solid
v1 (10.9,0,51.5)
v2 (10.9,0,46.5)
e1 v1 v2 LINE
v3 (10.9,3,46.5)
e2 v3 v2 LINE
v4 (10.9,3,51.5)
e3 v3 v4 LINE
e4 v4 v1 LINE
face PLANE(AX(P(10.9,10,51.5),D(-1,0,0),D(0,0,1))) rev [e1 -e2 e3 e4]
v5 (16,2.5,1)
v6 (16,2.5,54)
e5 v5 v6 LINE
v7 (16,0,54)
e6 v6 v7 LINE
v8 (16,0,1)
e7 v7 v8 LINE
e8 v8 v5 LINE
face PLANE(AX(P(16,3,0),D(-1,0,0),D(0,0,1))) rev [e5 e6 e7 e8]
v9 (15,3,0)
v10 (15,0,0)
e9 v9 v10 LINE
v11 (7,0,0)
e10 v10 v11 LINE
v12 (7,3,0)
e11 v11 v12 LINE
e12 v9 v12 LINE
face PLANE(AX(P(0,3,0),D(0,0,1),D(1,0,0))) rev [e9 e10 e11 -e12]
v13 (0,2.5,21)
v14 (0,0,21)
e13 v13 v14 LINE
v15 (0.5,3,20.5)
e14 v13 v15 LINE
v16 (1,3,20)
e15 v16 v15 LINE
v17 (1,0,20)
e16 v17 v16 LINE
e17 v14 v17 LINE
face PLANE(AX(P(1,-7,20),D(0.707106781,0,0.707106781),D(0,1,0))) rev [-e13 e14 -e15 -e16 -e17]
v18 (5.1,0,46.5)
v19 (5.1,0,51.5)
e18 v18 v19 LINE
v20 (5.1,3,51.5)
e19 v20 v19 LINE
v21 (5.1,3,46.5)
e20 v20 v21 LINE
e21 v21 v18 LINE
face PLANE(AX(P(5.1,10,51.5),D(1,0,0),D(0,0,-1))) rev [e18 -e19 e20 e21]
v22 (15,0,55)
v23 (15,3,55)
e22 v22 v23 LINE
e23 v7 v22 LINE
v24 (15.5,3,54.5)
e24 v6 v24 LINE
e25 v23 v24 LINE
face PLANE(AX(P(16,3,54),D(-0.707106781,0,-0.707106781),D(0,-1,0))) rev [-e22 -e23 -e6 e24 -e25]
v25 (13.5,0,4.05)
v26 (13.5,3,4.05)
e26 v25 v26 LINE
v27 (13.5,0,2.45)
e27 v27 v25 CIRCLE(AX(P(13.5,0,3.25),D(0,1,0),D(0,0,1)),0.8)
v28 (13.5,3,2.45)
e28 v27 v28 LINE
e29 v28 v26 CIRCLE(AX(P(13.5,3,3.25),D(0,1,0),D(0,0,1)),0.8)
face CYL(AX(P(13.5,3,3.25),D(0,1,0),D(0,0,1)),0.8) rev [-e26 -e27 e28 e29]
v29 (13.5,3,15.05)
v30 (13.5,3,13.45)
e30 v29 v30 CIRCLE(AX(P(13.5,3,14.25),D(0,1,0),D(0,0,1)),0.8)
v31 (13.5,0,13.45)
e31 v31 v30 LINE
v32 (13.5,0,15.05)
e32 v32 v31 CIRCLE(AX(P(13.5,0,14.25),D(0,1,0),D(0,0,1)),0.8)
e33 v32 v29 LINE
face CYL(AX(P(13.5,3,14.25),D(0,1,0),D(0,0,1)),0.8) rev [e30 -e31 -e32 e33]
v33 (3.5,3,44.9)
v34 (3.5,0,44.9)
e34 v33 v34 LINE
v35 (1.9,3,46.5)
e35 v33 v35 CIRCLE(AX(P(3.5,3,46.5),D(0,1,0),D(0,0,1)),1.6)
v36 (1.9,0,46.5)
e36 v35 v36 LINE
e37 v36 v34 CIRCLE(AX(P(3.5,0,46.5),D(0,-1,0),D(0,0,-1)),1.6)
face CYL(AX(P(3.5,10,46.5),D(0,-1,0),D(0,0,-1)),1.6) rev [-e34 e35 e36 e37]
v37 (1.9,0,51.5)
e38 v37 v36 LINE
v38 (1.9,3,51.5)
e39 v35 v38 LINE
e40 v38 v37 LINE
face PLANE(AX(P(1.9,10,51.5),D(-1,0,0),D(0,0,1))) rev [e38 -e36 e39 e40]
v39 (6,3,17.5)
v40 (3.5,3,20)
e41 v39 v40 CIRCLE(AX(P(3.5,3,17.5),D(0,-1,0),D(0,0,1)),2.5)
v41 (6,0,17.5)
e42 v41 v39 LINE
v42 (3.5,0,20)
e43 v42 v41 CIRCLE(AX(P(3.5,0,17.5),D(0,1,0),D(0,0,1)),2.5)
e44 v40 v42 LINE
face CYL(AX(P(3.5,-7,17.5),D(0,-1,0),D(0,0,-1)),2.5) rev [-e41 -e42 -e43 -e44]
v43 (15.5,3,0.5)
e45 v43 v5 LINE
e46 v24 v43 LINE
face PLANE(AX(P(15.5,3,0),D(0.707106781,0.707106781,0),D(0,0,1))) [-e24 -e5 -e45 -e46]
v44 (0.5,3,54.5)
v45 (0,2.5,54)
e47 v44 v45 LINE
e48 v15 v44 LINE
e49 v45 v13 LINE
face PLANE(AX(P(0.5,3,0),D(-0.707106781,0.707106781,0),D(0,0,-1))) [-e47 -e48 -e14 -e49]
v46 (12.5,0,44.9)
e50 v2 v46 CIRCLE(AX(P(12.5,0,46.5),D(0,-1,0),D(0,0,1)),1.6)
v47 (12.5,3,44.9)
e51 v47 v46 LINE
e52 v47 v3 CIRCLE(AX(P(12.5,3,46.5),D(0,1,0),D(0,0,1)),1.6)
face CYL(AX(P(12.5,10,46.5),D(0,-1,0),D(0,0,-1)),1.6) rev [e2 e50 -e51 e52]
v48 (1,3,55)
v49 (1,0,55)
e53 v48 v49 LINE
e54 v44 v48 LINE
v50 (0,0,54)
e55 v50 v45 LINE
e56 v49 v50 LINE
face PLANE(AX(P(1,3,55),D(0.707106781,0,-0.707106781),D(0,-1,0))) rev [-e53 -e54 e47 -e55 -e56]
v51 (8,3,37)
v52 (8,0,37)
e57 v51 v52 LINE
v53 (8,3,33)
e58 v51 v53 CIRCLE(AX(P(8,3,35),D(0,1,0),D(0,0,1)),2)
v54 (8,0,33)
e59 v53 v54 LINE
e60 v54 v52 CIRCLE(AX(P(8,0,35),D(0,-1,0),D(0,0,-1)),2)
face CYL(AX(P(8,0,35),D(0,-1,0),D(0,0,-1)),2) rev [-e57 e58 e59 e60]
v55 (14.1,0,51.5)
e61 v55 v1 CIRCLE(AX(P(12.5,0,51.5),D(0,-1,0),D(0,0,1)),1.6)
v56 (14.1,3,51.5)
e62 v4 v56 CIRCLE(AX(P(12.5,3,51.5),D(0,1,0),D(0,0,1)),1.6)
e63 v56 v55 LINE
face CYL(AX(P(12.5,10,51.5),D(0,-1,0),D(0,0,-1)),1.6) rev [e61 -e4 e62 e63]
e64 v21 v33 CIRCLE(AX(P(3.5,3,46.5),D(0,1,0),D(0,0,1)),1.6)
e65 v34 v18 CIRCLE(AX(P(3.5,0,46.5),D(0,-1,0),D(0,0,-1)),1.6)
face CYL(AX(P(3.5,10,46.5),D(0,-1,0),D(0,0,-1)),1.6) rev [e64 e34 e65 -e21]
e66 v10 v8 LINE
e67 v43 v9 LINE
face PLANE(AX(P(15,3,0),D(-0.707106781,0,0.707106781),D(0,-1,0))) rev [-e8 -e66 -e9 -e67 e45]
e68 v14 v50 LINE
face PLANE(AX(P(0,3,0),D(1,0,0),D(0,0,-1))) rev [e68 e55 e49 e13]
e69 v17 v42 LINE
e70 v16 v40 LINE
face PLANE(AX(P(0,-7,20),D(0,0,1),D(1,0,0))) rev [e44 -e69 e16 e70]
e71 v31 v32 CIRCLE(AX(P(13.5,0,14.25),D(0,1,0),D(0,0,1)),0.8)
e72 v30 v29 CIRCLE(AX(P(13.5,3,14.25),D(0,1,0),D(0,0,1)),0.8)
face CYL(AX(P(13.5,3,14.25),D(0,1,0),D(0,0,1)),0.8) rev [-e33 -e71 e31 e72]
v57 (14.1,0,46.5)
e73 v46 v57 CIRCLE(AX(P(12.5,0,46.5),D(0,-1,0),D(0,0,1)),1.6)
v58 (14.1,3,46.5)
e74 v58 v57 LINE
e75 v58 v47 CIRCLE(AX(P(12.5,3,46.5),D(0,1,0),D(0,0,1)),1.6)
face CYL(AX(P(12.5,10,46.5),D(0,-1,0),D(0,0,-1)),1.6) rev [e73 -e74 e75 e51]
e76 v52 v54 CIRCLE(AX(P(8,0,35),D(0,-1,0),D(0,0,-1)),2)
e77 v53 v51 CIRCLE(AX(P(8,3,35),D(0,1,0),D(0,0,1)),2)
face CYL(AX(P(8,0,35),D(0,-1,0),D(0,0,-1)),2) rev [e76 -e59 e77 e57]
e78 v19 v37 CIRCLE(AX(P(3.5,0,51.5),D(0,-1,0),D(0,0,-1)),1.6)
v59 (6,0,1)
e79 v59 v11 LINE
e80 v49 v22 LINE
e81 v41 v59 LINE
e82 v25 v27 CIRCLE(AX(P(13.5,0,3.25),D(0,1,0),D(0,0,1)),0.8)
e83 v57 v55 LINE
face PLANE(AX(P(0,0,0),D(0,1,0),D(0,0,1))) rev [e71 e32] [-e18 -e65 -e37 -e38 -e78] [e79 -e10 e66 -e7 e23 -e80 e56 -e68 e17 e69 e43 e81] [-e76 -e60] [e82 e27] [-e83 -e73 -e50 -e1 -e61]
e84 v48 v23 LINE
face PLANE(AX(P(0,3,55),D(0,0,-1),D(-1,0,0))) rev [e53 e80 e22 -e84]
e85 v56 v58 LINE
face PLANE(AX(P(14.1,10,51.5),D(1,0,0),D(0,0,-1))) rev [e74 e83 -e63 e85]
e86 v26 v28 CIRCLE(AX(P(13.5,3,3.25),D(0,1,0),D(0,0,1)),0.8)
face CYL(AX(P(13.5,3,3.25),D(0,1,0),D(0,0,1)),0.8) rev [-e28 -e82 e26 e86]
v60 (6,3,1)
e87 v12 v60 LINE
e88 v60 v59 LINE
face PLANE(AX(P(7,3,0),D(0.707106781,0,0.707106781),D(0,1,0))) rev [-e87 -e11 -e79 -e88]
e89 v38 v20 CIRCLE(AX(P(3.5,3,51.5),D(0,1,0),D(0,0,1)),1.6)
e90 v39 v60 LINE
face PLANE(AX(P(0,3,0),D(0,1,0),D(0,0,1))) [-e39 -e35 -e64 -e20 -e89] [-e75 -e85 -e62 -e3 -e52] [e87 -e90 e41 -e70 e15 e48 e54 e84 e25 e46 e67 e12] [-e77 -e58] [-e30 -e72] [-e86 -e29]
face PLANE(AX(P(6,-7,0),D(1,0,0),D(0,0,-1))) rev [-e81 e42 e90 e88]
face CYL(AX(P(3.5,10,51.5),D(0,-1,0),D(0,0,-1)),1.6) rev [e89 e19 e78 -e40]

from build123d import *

# Parameters (mm, degrees)
SKETCH1_W                    = 16
SKETCH1_H                    = 55
BOSS_EXTRUDE1_DEPTH          = 3
CUT_EXTRUDE2_DEPTH           = 10
SKETCH5_W                    = 6
SKETCH5_H                    = 20
CUT_EXTRUDE3_DEPTH           = 10
FILLET1_R                    = 2.5
CHAMFER1_SIZE                = 1
CHAMFER2_SIZE                = 0.5
M2_TAPPED_HOLE1_D            = 1.6
M2_TAPPED_HOLE1_DEPTH        = 5.2
M2_TAPPED_HOLE1_TIP          = 0.480688495
F_4_0_4_DIAMETER_HOLE1_D     = 4
F_4_0_4_DIAMETER_HOLE1_DEPTH = 4
F_4_0_4_DIAMETER_HOLE1_TIP   = 1.201721238


with BuildPart() as part:
    # Sketch1 → Boss-Extrude1 (new body)
    with BuildSketch(Plane(origin=(0, 0, 0), x_dir=(1, 0, 0), z_dir=(0, 1, 0))):
        with Locations((8, -27.5)):
            Rectangle(SKETCH1_W, SKETCH1_H)
    extrude(amount=BOSS_EXTRUDE1_DEPTH)

    # Sketch4 → Cut-Extrude2 (cut)
    with BuildSketch(Plane.XZ):
        with BuildLine():
            Line((5.1, 51.5), (5.1, 46.5))
            ThreePointArc((5.1, 46.5), (3.5, 44.9), (1.9, 46.5))
            Line((1.9, 46.5), (1.9, 51.5))
            ThreePointArc((1.9, 51.5), (3.5, 53.1), (5.1, 51.5))
        make_face()
        with BuildLine():
            Line((10.9, 51.5), (10.9, 46.5))
            ThreePointArc((10.9, 46.5), (12.5, 44.9), (14.1, 46.5))
            Line((14.1, 46.5), (14.1, 51.5))
            ThreePointArc((14.1, 51.5), (12.5, 53.1), (10.9, 51.5))
        make_face()
    extrude(amount=-CUT_EXTRUDE2_DEPTH, mode=Mode.SUBTRACT)

    # Sketch5 → Cut-Extrude3 (cut)
    with BuildSketch(Plane(origin=(0, 3, 0), x_dir=(1, 0, 0), z_dir=(0, 1, 0))):
        with Locations((3, -10)):
            Rectangle(SKETCH5_W, SKETCH5_H)
    extrude(amount=-CUT_EXTRUDE3_DEPTH, mode=Mode.SUBTRACT)

    # Fillet1
    fillet1_edges = [part.edges().sort_by_distance(p)[0] for p in [
        (6, 1.5, 20),
    ]]
    fillet(fillet1_edges, radius=FILLET1_R)

    # Chamfer1
    chamfer1_edges = [part.edges().sort_by_distance(p)[0] for p in [
        (0, 1.5, 20),
        (6, 1.5, 0),
        (16, 1.5, 0),
        (16, 1.5, 55),
        (0, 1.5, 55),
    ]]
    chamfer(chamfer1_edges, length=CHAMFER1_SIZE)

    # Chamfer2
    chamfer2_edges = [part.edges().sort_by_distance(p)[0] for p in [
        (0, 3, 37.5),
        (16, 3, 27.5),
    ]]
    chamfer(chamfer2_edges, length=CHAMFER2_SIZE)

    # M2 Tapped Hole1
    with Locations(Plane(origin=(0, 3, 0), x_dir=(1, 0, 0), z_dir=(0, 1, 0))):
        with Locations((13.5, -3.25), (13.5, -14.25)):
            Hole(M2_TAPPED_HOLE1_D / 2, depth=M2_TAPPED_HOLE1_DEPTH)
            with Locations((0, 0, -(M2_TAPPED_HOLE1_DEPTH + M2_TAPPED_HOLE1_TIP / 2))):  # 118° drill point
                Cone(0, M2_TAPPED_HOLE1_D / 2, M2_TAPPED_HOLE1_TIP, mode=Mode.SUBTRACT)

    # Ø4.0 (4) Diameter Hole1
    with Locations(Plane(origin=(0, 0, 0), x_dir=(-1, 0, 0), z_dir=(0, -1, 0))):
        with Locations((-8, -35)):
            Hole(F_4_0_4_DIAMETER_HOLE1_D / 2, depth=F_4_0_4_DIAMETER_HOLE1_DEPTH)
            with Locations((0, 0, -(F_4_0_4_DIAMETER_HOLE1_DEPTH + F_4_0_4_DIAMETER_HOLE1_TIP / 2))):  # 118° drill point
                Cone(0, F_4_0_4_DIAMETER_HOLE1_D / 2, F_4_0_4_DIAMETER_HOLE1_TIP, mode=Mode.SUBTRACT)


solid = part.part
